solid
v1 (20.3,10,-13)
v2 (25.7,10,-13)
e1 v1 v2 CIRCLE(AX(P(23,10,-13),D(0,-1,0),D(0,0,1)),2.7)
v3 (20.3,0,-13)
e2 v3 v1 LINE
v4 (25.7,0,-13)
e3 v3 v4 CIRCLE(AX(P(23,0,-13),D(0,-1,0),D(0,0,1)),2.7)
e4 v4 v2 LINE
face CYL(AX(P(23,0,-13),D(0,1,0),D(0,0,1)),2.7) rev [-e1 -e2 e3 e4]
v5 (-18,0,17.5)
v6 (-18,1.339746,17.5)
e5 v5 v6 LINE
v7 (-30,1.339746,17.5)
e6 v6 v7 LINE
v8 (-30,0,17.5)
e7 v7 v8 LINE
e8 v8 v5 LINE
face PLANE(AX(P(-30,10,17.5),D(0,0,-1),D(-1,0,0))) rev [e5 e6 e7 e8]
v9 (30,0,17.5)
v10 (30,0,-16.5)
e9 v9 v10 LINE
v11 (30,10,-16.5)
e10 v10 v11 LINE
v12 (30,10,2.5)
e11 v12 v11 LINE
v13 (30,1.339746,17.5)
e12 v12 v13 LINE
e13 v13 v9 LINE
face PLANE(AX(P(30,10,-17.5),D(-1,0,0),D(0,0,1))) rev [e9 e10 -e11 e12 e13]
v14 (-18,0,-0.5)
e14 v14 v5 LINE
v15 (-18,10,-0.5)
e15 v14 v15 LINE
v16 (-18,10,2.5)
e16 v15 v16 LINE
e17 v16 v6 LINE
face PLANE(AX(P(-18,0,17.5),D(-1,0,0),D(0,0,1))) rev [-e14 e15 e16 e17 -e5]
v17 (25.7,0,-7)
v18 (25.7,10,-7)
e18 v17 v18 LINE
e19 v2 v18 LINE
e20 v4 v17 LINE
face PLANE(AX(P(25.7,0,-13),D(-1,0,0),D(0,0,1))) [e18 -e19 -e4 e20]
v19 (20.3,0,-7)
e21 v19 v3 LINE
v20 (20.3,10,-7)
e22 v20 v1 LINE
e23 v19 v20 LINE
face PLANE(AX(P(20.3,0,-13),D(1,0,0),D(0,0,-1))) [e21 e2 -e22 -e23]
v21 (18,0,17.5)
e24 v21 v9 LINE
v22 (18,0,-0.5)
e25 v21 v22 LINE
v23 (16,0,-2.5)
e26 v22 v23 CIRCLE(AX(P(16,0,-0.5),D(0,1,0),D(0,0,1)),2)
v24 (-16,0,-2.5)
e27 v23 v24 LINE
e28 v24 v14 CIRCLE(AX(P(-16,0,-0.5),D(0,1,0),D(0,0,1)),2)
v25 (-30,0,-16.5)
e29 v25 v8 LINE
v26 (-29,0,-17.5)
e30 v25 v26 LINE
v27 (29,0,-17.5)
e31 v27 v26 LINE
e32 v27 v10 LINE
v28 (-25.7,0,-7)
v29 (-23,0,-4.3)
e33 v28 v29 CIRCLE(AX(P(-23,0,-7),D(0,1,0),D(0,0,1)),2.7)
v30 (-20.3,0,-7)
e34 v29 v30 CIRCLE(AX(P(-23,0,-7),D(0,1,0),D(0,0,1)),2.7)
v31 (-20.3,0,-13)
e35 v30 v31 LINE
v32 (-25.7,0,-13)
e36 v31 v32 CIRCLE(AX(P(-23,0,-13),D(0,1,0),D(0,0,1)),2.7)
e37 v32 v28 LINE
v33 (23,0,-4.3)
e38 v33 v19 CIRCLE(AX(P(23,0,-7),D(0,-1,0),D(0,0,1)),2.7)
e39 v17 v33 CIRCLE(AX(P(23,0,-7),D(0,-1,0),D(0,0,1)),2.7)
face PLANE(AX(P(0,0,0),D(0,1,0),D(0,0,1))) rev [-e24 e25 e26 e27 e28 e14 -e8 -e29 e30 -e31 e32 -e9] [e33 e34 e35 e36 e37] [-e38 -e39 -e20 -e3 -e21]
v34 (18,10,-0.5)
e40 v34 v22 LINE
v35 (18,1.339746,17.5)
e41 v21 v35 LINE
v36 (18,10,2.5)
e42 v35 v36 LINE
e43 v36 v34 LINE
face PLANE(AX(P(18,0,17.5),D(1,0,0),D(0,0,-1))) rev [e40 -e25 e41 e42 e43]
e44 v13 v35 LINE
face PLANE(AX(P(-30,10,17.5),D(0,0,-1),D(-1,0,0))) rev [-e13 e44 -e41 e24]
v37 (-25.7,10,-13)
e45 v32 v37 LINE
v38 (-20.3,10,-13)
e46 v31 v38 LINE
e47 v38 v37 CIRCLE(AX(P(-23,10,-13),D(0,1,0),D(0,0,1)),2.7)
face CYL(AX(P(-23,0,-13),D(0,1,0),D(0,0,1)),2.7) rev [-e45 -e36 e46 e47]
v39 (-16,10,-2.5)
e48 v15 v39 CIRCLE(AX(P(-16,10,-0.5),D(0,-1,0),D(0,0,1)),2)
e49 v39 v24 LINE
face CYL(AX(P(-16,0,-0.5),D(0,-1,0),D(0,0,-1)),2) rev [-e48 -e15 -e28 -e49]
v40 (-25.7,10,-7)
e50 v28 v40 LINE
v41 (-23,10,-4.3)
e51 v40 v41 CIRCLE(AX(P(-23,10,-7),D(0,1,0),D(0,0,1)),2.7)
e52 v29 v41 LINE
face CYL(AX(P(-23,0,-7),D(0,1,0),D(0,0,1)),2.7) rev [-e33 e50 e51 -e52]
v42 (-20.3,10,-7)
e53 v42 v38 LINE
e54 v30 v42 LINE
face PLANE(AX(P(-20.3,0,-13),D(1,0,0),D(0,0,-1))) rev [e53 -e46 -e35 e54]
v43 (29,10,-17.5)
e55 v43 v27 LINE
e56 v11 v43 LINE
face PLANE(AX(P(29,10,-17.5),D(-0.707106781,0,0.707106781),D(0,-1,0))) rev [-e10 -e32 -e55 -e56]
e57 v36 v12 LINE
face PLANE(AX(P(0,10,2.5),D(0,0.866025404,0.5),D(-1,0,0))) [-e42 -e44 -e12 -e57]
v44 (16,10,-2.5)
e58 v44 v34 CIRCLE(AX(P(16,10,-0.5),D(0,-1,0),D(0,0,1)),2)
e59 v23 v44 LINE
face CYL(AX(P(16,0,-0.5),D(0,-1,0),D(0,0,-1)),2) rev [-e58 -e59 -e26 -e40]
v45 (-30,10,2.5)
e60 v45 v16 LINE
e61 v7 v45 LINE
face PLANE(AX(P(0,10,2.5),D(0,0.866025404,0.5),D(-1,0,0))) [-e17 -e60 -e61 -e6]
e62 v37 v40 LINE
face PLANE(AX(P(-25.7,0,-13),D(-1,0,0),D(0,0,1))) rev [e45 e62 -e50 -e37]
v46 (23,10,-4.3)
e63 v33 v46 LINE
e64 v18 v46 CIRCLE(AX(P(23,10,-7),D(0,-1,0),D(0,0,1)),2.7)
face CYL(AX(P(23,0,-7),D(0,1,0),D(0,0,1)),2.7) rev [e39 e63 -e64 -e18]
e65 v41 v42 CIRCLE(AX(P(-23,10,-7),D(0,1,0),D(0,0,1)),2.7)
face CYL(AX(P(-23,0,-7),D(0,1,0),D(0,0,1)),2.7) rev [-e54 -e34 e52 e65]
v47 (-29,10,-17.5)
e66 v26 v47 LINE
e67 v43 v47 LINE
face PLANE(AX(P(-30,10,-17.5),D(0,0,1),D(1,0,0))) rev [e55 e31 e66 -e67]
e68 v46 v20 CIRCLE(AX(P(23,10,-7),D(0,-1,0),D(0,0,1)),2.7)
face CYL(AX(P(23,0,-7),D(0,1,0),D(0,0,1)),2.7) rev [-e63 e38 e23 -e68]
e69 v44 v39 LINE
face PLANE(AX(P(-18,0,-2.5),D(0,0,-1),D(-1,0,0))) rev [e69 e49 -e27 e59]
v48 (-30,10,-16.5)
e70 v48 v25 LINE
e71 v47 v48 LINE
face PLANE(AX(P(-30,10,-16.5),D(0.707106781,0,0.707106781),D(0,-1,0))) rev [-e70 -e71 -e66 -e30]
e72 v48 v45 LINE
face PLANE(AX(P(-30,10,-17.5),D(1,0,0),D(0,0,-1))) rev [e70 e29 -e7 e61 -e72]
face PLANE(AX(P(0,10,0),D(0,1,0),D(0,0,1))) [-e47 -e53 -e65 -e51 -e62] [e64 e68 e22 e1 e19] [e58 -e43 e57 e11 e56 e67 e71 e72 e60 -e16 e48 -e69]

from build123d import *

# Parameters (mm, degrees)
SKETCH1_W           = 60
SKETCH1_H           = 35
BOSS_EXTRUDE1_DEPTH = 10
CHAMFER1_SIZE       = 15
CHAMFER1_SIZE2      = 8.660254038
SKETCH2_W           = 36
SKETCH2_H           = 20
CUT_EXTRUDE1_DEPTH  = 37.142080737
FILLET1_R           = 2
CUT_EXTRUDE2_DEPTH  = 37.142080737
CHAMFER2_SIZE       = 1


with BuildPart() as part:
    # Sketch1 → Boss-Extrude1 (new body)
    with BuildSketch(Plane(origin=(0, 0, 0), x_dir=(1, 0, 0), z_dir=(0, 1, 0))):
        Rectangle(SKETCH1_W, SKETCH1_H)
    extrude(amount=BOSS_EXTRUDE1_DEPTH)

    # Chamfer1
    chamfer1_edges = [part.edges().sort_by_distance(p)[0] for p in [
        (0, 10, 17.5),
    ]]
    chamfer1_side = [part.faces().sort_by_distance(p)[0] for p in [
        (0, 10, 0),
    ]]
    chamfer(chamfer1_edges, length=CHAMFER1_SIZE, length2=CHAMFER1_SIZE2, reference=chamfer1_side[0])

    # Sketch2 → Cut-Extrude1 (cut, through all)
    with BuildSketch(Plane(origin=(0, 10, 0), x_dir=(1, 0, 0), z_dir=(0, 1, 0))):
        with Locations((0, -7.5)):
            Rectangle(SKETCH2_W, SKETCH2_H)
    extrude(amount=-CUT_EXTRUDE1_DEPTH, mode=Mode.SUBTRACT)

    # Fillet1
    fillet1_edges = [part.edges().sort_by_distance(p)[0] for p in [
        (-18, 5, -2.5),
        (18, 5, -2.5),
    ]]
    fillet(fillet1_edges, radius=FILLET1_R)

    # Sketch3 → Cut-Extrude2 (cut, through all)
    with BuildSketch(Plane(origin=(0, 10, 0), x_dir=(1, 0, 0), z_dir=(0, 1, 0))):
        with BuildLine():
            Line((-20.3, 13), (-20.3, 7))
            ThreePointArc((-20.3, 7), (-23, 4.3), (-25.7, 7))
            Line((-25.7, 7), (-25.7, 13))
            ThreePointArc((-25.7, 13), (-23, 15.7), (-20.3, 13))
        make_face()
    cut_extrude2 = extrude(amount=-CUT_EXTRUDE2_DEPTH, mode=Mode.SUBTRACT)

    # Mirror1: Cut-Extrude2 across plane
    add(cut_extrude2.mirror(Plane(origin=(0, 0, 0), x_dir=(0, 0, 1), z_dir=(1, 0, 0))), mode=Mode.SUBTRACT)

    # Chamfer2
    chamfer2_edges = [part.edges().sort_by_distance(p)[0] for p in [
        (-30, 5, -17.5),
        (30, 5, -17.5),
    ]]
    chamfer(chamfer2_edges, length=CHAMFER2_SIZE)


solid = part.part
